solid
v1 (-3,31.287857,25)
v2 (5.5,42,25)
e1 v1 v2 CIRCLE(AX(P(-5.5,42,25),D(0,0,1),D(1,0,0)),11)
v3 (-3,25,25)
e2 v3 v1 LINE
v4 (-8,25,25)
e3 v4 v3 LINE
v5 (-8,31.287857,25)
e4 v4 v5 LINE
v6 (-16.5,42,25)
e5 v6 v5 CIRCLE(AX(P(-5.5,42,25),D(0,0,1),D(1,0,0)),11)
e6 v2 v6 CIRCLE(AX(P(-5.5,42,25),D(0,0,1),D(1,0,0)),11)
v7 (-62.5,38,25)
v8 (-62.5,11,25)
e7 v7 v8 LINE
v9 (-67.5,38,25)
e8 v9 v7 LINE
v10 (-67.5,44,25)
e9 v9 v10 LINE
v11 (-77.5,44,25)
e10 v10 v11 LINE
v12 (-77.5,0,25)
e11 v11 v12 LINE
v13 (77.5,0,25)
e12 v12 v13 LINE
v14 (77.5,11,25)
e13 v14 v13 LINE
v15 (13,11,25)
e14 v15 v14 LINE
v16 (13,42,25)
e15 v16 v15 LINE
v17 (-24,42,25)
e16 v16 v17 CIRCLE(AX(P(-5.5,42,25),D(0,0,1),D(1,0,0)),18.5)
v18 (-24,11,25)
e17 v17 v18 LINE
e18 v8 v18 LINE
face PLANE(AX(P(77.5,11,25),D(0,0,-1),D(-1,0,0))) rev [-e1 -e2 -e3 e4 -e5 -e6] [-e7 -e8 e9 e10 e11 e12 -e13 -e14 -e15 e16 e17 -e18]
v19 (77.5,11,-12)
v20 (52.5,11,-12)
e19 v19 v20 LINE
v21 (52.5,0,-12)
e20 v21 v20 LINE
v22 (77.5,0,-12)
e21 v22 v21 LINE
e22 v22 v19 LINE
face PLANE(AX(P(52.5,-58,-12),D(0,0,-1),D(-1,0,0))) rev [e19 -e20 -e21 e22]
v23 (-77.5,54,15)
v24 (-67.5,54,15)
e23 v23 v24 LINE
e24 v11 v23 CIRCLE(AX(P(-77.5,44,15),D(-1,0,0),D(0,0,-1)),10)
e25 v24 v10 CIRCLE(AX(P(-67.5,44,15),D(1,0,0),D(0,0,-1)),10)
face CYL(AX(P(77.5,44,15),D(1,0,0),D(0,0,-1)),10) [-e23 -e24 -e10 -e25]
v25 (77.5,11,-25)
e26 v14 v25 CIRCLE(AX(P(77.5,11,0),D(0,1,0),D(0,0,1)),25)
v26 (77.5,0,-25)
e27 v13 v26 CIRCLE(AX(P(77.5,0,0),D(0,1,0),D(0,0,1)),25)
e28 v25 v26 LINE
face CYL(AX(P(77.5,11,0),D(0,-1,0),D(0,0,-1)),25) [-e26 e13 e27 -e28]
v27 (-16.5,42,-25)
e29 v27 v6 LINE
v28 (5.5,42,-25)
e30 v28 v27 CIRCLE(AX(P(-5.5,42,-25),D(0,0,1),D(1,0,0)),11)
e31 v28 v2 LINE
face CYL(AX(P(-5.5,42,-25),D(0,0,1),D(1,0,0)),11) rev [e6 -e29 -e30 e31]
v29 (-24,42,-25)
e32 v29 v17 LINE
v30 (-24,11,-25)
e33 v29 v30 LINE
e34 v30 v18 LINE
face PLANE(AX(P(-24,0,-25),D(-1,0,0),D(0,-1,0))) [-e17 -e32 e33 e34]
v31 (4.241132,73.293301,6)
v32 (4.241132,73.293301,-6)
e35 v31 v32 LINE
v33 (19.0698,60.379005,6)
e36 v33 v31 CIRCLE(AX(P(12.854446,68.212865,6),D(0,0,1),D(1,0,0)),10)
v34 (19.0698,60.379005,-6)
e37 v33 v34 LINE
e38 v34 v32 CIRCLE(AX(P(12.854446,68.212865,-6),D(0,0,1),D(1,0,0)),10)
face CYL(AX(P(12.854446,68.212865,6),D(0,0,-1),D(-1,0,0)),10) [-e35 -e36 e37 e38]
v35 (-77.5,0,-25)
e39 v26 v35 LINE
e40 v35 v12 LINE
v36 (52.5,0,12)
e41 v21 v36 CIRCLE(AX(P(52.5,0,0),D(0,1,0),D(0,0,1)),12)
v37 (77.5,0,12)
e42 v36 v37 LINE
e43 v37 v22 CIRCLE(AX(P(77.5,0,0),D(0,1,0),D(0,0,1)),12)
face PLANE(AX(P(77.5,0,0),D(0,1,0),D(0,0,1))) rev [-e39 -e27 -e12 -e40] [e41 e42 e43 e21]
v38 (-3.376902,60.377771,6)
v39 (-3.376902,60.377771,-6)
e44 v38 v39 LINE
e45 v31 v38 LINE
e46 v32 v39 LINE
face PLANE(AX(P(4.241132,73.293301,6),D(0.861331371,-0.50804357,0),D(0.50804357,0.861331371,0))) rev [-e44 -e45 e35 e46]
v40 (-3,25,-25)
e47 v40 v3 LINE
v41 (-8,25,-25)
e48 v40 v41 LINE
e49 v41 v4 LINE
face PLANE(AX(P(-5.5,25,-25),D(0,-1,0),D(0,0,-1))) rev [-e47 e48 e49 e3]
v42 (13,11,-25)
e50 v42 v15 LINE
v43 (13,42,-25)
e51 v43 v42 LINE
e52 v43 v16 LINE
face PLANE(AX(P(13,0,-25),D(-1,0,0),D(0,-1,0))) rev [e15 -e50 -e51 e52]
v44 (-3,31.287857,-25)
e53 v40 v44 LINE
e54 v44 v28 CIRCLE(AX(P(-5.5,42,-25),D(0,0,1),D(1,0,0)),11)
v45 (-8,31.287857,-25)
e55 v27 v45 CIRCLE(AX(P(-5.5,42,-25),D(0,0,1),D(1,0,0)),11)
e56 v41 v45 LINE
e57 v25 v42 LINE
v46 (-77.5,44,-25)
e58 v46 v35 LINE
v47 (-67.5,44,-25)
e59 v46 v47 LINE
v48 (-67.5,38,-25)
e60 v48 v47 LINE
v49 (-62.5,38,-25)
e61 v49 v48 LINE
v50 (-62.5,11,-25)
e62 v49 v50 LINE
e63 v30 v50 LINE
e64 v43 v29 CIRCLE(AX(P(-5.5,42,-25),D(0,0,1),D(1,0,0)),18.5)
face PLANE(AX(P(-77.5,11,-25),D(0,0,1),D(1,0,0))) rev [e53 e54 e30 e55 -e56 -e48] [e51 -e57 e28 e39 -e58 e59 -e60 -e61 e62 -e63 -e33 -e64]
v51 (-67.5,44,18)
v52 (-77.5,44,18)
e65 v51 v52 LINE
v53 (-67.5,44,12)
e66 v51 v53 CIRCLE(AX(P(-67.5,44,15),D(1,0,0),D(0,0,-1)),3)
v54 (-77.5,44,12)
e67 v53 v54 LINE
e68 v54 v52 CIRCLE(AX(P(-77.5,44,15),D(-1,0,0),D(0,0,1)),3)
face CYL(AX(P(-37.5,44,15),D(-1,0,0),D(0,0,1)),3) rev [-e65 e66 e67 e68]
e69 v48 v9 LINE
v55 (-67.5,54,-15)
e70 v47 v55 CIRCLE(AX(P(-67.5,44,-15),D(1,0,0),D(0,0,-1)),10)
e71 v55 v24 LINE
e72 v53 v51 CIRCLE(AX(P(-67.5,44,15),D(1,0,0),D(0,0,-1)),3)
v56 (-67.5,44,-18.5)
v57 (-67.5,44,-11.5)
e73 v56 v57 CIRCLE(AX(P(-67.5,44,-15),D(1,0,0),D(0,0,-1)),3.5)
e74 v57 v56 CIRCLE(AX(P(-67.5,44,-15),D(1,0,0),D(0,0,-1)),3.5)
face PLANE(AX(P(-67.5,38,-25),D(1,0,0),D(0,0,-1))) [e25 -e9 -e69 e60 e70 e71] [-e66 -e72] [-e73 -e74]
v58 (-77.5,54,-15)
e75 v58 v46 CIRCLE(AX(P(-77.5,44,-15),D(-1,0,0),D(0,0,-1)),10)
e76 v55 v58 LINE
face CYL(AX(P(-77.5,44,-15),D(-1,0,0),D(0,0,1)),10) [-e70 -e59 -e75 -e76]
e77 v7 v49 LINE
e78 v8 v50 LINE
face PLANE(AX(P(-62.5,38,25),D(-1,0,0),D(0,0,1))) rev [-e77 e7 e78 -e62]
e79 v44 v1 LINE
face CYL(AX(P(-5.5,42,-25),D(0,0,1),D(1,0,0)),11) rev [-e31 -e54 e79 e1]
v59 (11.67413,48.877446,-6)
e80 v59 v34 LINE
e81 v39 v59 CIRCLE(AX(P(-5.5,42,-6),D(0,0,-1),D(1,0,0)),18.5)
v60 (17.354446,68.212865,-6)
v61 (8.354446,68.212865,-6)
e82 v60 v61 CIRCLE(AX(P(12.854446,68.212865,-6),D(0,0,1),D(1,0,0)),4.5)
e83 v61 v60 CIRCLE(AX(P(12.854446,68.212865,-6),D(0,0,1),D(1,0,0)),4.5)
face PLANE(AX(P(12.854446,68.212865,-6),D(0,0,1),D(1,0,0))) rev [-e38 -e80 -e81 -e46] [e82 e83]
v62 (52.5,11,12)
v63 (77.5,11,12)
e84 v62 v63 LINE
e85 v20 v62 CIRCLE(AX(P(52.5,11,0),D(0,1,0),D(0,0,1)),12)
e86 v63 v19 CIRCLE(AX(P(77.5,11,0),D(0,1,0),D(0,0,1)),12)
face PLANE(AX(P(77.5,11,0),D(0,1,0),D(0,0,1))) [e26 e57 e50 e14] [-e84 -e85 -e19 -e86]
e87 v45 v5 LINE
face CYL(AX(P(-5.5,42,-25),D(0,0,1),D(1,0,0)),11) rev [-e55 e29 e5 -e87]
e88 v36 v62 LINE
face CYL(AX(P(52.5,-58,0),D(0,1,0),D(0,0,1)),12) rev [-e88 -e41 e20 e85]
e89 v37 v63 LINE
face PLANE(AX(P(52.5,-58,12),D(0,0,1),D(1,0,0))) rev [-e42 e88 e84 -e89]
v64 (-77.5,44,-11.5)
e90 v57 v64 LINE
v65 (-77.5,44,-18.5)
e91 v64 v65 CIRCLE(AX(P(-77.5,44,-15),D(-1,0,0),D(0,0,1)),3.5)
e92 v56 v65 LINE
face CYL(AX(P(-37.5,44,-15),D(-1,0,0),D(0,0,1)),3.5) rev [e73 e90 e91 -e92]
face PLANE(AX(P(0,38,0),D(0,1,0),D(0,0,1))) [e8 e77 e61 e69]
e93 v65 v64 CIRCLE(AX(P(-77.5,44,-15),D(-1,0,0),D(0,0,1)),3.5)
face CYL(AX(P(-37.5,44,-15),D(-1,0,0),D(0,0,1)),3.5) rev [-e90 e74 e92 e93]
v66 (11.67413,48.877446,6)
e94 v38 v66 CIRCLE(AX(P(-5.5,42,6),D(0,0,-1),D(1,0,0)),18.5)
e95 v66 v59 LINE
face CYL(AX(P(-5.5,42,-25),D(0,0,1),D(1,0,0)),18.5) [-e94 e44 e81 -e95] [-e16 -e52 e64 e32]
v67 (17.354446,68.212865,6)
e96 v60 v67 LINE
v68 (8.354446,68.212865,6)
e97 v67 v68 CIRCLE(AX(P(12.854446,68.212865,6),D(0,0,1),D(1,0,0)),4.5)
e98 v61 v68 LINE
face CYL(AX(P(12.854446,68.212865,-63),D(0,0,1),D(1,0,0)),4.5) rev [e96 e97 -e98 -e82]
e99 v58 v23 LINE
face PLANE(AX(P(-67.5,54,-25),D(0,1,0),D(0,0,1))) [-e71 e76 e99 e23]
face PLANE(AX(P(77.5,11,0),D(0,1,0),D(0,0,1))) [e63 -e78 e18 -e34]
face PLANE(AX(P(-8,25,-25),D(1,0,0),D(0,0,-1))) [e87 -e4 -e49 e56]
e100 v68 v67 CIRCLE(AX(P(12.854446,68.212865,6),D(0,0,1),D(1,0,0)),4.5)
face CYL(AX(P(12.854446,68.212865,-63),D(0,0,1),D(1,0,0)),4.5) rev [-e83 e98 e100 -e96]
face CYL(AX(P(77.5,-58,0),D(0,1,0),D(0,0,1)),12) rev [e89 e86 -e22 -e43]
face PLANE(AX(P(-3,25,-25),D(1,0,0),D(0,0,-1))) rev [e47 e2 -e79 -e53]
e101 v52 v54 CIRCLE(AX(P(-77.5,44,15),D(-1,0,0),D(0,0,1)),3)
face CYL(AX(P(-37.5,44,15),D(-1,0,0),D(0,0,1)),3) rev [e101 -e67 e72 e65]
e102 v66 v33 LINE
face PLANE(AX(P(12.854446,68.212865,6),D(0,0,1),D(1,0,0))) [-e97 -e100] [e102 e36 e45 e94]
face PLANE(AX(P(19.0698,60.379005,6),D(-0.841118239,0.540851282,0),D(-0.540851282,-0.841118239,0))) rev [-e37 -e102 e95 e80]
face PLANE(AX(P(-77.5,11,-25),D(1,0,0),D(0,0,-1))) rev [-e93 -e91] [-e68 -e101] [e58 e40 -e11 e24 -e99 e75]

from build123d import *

# Parameters (mm, degrees)
BASE_PLATE_11MM_DEPTH    = 11
UPRIGHT_BLOCK_DEPTH      = 50
CHANNEL_CUT_DEPTH        = 50
FRONT_WALL_12MM_DEPTH    = 6
WALL_HOLE_SKETCH_R       = 4.5
WALL_THROUGH_HOLE_DEPTH  = 69
BORE_KEYWAY_CUT_DEPTH    = 69
HOUSING_PAD_SKETCH_W     = 15
HOUSING_PAD_SKETCH_H     = 50
HOUSING_PAD_DEPTH        = 27
BORE_HOUSING_SKETCH_W    = 10
BORE_HOUSING_SKETCH_H    = 16
BORE_HOUSING_DEPTH       = 50
HOUSING_FILLET_R10_A_R   = 10
HOUSING_FILLET_R10_B_R   = 10
CROSS_HOLE_SKETCH_R      = 3.5
CROSS_HOLE_SKETCH_R_2    = 3
HOUSING_CROSS_HOLE_DEPTH = 40


with BuildPart() as part:
    # Base Plate Sketch → Base Plate 11mm (new body)
    with BuildSketch(Plane(origin=(0, 0, 0), x_dir=(1, 0, 0), z_dir=(0, 1, 0))):
        with BuildLine():
            Line((-77.5, 25), (-77.5, -25))
            Line((-77.5, -25), (77.5, -25))
            ThreePointArc((77.5, -25), (102.5, 0), (77.5, 25))
            Line((77.5, 25), (-77.5, 25))
        make_face()
    extrude(amount=BASE_PLATE_11MM_DEPTH)

    # Upright Block Sketch → Upright Block (add)
    with BuildSketch(Plane.XY.offset(25)):
        with BuildLine():
            ThreePointArc((13, 42), (-5.5, 60.5), (-24, 42))
            Line((-24, 42), (-24, 11))
            Line((-24, 11), (13, 11))
            Line((13, 11), (13, 42))
        make_face()
    extrude(amount=-UPRIGHT_BLOCK_DEPTH)

    # Channel Cut Sketch → Channel Cut (cut)
    with BuildSketch(Plane.XY.offset(25)):
        with BuildLine():
            Line((-5.5, 25), (-8, 25))
            Line((-8, 25), (-8, 31.287857357))
            ThreePointArc((-8, 31.287857357), (-5.5, 53), (-3, 31.287857357))
            Line((-3, 31.287857357), (-3, 25))
            Line((-3, 25), (-5.5, 25))
        make_face()
    extrude(amount=-CHANNEL_CUT_DEPTH, mode=Mode.SUBTRACT)

    # Front Wall Sketch → Front Wall 12mm (add, symmetric)
    with BuildSketch(Plane.XY):
        with BuildLine():
            Line((4.241132249, 73.293301112), (-3.376902326, 60.37777071))
            Line((-3.376902326, 60.37777071), (11.674130016, 48.877445616))
            Line((11.674130016, 48.877445616), (19.069800109, 60.379004757))
            ThreePointArc((19.069800109, 60.379004757), (19.421965671, 75.753931979), (4.241132249, 73.293301112))
        make_face()
    extrude(amount=FRONT_WALL_12MM_DEPTH, both=True)

    # Wall Hole Sketch → Wall Through Hole (cut)
    with BuildSketch(Plane.XY.offset(6)):
        with Locations((12.854445963, 68.212865417)):
            Circle(WALL_HOLE_SKETCH_R)
    extrude(amount=-WALL_THROUGH_HOLE_DEPTH, mode=Mode.SUBTRACT)

    # Bore Keyway Sketch → Bore Keyway Cut (cut)
    with BuildSketch(Plane(origin=(0, 11, 0), x_dir=(1, 0, 0), z_dir=(0, 1, 0))):
        with BuildLine():
            Line((52.5, 12), (77.5, 12))
            ThreePointArc((77.5, 12), (89.5, 0), (77.5, -12))
            Line((77.5, -12), (52.5, -12))
            ThreePointArc((52.5, -12), (40.5, 0), (52.5, 12))
        make_face()
    extrude(amount=-BORE_KEYWAY_CUT_DEPTH, mode=Mode.SUBTRACT)

    # Housing Pad Sketch → Housing Pad (add)
    with BuildSketch(Plane(origin=(0, 11, 0), x_dir=(1, 0, 0), z_dir=(0, 1, 0))):
        with Locations((-70, 0)):
            Rectangle(HOUSING_PAD_SKETCH_W, HOUSING_PAD_SKETCH_H)
    extrude(amount=HOUSING_PAD_DEPTH)

    # Bore Housing Sketch → Bore Housing (add)
    with BuildSketch(Plane.XY.offset(25)):
        with Locations((-72.5, 46)):
            Rectangle(BORE_HOUSING_SKETCH_W, BORE_HOUSING_SKETCH_H)
    extrude(amount=-BORE_HOUSING_DEPTH)

    # Housing Fillet R10 A
    housing_fillet_r10_a_edges = [part.edges().sort_by_distance(p)[0] for p in [
        (-72.5, 54, 25),
    ]]
    fillet(housing_fillet_r10_a_edges, radius=HOUSING_FILLET_R10_A_R)

    # Housing Fillet R10 B
    housing_fillet_r10_b_edges = [part.edges().sort_by_distance(p)[0] for p in [
        (-72.5, 54, -25),
    ]]
    fillet(housing_fillet_r10_b_edges, radius=HOUSING_FILLET_R10_B_R)

    # Cross Hole Sketch → Housing Cross Hole (cut)
    with BuildSketch(Plane.ZY.offset(77.5)):
        with Locations((-15, 44)):
            Circle(CROSS_HOLE_SKETCH_R)
        with Locations((15, 44)):
            Circle(CROSS_HOLE_SKETCH_R_2)
    extrude(amount=-HOUSING_CROSS_HOLE_DEPTH, mode=Mode.SUBTRACT)


solid = part.part
